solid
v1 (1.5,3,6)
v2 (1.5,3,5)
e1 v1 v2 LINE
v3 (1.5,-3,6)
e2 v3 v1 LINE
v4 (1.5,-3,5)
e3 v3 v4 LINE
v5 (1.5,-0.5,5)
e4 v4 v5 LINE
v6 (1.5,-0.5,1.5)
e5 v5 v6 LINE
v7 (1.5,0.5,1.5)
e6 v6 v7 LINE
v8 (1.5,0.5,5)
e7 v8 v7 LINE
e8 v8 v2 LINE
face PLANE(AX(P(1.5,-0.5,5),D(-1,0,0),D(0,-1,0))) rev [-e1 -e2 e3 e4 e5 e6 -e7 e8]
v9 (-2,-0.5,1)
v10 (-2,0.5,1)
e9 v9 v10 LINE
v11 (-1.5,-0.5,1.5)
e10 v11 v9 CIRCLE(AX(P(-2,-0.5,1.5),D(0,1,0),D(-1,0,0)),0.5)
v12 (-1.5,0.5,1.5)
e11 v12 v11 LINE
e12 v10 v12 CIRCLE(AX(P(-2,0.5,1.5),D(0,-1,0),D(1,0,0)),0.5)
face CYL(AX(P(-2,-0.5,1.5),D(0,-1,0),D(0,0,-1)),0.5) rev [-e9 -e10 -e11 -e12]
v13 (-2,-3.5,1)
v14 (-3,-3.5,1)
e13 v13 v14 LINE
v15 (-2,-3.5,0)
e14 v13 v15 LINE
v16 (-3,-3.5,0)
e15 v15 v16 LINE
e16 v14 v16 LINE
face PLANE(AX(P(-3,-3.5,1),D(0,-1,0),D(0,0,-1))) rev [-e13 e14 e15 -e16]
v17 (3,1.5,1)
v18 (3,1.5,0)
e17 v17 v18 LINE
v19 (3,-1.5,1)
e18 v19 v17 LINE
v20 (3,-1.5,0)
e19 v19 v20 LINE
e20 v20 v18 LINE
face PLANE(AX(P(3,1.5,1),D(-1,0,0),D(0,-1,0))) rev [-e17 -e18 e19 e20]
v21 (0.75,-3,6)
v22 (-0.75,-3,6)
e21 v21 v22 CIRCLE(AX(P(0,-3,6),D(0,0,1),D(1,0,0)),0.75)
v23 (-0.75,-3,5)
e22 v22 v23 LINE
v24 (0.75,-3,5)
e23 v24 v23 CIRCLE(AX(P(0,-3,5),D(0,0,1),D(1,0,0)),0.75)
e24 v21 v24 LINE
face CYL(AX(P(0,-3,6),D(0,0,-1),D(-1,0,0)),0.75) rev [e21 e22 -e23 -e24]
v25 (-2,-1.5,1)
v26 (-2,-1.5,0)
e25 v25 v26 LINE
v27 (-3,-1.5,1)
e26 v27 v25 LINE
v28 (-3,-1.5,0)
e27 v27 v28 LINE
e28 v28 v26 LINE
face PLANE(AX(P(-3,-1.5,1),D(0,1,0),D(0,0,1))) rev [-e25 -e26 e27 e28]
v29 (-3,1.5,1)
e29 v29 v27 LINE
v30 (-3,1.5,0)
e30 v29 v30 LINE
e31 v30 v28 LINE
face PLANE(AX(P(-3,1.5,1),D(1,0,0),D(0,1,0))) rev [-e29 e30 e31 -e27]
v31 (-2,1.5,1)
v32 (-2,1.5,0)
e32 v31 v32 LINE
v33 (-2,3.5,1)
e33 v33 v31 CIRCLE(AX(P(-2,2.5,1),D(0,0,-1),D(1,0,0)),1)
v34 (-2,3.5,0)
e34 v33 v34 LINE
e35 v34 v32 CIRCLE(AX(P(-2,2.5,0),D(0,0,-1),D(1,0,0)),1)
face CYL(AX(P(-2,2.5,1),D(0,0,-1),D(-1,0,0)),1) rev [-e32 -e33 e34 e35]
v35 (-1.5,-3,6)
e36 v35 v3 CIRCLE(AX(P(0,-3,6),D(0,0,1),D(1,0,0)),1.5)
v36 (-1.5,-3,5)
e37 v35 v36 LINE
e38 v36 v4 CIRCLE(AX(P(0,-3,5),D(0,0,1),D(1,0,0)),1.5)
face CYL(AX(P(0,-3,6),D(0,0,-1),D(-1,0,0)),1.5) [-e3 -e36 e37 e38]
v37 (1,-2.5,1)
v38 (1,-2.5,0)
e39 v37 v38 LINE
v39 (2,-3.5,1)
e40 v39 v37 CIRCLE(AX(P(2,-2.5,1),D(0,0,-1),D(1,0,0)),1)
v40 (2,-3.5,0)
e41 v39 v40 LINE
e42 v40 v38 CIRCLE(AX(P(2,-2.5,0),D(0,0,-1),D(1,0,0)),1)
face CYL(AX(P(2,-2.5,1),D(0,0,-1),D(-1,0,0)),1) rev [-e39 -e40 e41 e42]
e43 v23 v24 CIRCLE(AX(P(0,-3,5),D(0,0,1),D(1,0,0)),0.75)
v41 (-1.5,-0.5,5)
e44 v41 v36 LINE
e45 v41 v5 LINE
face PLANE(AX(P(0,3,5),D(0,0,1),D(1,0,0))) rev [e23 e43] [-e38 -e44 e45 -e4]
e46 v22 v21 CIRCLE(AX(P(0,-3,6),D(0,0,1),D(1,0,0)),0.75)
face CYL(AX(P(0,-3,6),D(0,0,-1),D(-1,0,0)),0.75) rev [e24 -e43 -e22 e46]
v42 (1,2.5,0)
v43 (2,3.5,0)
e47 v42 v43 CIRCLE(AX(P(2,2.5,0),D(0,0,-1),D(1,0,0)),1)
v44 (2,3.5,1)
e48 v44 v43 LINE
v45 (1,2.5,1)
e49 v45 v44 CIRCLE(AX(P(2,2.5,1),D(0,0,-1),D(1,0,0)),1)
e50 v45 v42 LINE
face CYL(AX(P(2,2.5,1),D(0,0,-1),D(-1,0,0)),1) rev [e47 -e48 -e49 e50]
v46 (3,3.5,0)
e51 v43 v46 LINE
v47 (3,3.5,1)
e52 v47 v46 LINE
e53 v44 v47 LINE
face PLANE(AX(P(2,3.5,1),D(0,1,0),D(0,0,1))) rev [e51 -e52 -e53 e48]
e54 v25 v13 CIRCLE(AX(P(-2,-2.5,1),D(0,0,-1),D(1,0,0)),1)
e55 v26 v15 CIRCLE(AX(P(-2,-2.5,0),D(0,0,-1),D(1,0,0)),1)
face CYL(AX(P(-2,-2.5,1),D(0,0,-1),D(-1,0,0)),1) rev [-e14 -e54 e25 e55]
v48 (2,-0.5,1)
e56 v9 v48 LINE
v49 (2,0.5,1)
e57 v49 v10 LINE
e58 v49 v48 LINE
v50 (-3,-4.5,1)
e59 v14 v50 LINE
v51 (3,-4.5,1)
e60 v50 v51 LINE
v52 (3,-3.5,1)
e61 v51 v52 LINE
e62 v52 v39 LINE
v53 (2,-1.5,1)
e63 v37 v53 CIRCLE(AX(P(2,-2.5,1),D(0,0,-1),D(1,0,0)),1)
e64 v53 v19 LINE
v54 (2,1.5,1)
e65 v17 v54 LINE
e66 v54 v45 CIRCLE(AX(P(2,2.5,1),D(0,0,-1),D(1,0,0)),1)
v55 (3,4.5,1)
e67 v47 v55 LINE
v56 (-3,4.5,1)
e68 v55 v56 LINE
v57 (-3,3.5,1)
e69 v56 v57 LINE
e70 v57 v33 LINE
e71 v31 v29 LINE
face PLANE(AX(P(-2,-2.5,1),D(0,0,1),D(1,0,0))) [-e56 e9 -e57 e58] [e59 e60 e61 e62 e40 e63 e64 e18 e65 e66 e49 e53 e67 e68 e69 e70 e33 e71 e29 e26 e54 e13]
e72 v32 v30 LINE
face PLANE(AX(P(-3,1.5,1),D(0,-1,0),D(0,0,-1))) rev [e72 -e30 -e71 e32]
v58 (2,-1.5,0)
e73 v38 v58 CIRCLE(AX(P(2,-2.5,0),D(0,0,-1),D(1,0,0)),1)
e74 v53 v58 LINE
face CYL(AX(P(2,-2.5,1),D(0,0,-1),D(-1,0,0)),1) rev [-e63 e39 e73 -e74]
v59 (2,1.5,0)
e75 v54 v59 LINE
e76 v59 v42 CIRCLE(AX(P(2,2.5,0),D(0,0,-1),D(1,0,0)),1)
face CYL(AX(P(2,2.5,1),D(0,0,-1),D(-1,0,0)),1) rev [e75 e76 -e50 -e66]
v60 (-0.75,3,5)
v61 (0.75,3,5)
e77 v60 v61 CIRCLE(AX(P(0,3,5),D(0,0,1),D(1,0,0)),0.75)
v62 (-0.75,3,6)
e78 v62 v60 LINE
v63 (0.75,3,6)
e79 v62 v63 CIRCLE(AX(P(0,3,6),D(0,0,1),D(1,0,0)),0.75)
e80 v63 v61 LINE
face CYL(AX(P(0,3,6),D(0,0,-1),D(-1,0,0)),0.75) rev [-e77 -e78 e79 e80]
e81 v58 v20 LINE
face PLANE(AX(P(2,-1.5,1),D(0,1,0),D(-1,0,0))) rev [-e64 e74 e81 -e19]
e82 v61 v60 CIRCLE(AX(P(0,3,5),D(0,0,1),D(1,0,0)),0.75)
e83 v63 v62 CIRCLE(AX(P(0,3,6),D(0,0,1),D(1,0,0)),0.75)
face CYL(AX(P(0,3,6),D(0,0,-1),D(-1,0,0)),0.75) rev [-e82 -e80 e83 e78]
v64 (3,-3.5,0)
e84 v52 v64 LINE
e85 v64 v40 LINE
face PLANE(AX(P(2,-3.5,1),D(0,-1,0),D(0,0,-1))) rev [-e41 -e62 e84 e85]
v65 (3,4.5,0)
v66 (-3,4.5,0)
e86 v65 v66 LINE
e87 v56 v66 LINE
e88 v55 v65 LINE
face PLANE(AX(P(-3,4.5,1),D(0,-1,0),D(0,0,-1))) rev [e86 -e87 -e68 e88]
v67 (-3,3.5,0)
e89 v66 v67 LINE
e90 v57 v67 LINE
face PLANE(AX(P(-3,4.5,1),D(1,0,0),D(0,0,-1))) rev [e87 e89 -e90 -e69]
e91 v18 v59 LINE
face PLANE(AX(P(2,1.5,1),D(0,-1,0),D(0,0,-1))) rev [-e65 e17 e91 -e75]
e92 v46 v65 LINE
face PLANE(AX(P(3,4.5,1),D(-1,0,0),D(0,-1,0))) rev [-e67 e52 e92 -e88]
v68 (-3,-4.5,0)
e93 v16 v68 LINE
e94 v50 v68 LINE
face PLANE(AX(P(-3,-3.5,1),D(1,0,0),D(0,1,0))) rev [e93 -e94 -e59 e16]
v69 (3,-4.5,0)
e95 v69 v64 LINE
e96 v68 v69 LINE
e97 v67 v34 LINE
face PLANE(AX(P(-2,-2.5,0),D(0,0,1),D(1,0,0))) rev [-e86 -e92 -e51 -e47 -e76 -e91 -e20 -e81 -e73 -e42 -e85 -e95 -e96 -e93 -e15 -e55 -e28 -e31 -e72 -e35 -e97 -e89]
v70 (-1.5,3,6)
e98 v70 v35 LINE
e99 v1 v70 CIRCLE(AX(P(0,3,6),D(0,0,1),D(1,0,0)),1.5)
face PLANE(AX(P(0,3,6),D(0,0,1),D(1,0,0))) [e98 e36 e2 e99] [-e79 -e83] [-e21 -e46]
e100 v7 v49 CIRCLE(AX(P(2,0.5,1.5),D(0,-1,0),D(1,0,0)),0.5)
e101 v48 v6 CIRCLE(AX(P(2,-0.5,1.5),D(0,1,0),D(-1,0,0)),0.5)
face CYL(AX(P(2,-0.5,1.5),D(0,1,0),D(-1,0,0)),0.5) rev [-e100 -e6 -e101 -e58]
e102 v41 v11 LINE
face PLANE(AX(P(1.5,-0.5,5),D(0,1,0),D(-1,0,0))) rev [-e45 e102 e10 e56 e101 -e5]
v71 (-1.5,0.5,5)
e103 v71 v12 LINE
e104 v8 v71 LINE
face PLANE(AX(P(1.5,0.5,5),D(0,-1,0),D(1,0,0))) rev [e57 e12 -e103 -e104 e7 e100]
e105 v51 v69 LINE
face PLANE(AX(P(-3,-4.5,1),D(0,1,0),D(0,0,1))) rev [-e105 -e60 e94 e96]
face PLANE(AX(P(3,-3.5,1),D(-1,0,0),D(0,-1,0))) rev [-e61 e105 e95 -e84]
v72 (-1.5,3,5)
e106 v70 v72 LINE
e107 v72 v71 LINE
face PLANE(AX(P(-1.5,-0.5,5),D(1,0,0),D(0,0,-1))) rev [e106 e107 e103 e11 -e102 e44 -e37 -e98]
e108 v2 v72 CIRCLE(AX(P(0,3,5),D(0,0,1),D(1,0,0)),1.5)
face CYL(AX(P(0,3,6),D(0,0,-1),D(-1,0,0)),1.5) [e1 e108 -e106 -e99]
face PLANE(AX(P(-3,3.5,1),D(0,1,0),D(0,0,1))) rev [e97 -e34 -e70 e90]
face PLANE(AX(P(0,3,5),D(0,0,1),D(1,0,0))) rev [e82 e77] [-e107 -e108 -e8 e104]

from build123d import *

# Parameters (mm, degrees)
BASE_PLATE_DEPTH         = 1
WEB_SKETCH_W             = 3
WEB_SKETCH_H             = 1
WEB_DEPTH                = 4
LINK_PLATE_SKETCH_R      = 0.75
LINK_PLATE_DEPTH         = 1
WEB_ROOT_FILLET_R0_5_A_R = 0.5
WEB_ROOT_FILLET_R0_5_B_R = 0.5


with BuildPart() as part:
    # Base Plate Sketch → Base Plate (new body)
    with BuildSketch(Plane.XY):
        with BuildLine():
            Line((-3, 3.5), (-2, 3.5))
            ThreePointArc((-2, 3.5), (-1, 2.5), (-2, 1.5))
            Line((-2, 1.5), (-3, 1.5))
            Line((-3, 1.5), (-3, -1.5))
            Line((-3, -1.5), (-2, -1.5))
            ThreePointArc((-2, -1.5), (-1, -2.5), (-2, -3.5))
            Line((-2, -3.5), (-3, -3.5))
            Line((-3, -3.5), (-3, -4.5))
            Line((-3, -4.5), (3, -4.5))
            Line((3, -4.5), (3, -3.5))
            Line((3, -3.5), (2, -3.5))
            ThreePointArc((2, -3.5), (1, -2.5), (2, -1.5))
            Line((2, -1.5), (3, -1.5))
            Line((3, -1.5), (3, 1.5))
            Line((3, 1.5), (2, 1.5))
            ThreePointArc((2, 1.5), (1, 2.5), (2, 3.5))
            Line((2, 3.5), (3, 3.5))
            Line((3, 3.5), (3, 4.5))
            Line((3, 4.5), (-3, 4.5))
            Line((-3, 4.5), (-3, 3.5))
        make_face()
    extrude(amount=BASE_PLATE_DEPTH)

    # Web Sketch → Web (add)
    with BuildSketch(Plane.XY.offset(1)):
        Rectangle(WEB_SKETCH_W, WEB_SKETCH_H)
    extrude(amount=WEB_DEPTH)

    # Link Plate Sketch → Link Plate (add)
    with BuildSketch(Plane.XY.offset(5)):
        with BuildLine():
            Line((1.5, 3), (1.5, -3))
            ThreePointArc((1.5, -3), (0, -4.5), (-1.5, -3))
            Line((-1.5, -3), (-1.5, 3))
            ThreePointArc((-1.5, 3), (0, 4.5), (1.5, 3))
        make_face()
        with Locations((0, 3)):
            Circle(LINK_PLATE_SKETCH_R, mode=Mode.SUBTRACT)
        with Locations((0, -3)):
            Circle(LINK_PLATE_SKETCH_R, mode=Mode.SUBTRACT)
    extrude(amount=LINK_PLATE_DEPTH)

    # Web Root Fillet R0.5 A
    web_root_fillet_r0_5_a_edges = [part.edges().sort_by_distance(p)[0] for p in [
        (1.5, 0, 1),
    ]]
    fillet(web_root_fillet_r0_5_a_edges, radius=WEB_ROOT_FILLET_R0_5_A_R)

    # Web Root Fillet R0.5 B
    web_root_fillet_r0_5_b_edges = [part.edges().sort_by_distance(p)[0] for p in [
        (-1.5, 0, 1),
    ]]
    fillet(web_root_fillet_r0_5_b_edges, radius=WEB_ROOT_FILLET_R0_5_B_R)


solid = part.part
